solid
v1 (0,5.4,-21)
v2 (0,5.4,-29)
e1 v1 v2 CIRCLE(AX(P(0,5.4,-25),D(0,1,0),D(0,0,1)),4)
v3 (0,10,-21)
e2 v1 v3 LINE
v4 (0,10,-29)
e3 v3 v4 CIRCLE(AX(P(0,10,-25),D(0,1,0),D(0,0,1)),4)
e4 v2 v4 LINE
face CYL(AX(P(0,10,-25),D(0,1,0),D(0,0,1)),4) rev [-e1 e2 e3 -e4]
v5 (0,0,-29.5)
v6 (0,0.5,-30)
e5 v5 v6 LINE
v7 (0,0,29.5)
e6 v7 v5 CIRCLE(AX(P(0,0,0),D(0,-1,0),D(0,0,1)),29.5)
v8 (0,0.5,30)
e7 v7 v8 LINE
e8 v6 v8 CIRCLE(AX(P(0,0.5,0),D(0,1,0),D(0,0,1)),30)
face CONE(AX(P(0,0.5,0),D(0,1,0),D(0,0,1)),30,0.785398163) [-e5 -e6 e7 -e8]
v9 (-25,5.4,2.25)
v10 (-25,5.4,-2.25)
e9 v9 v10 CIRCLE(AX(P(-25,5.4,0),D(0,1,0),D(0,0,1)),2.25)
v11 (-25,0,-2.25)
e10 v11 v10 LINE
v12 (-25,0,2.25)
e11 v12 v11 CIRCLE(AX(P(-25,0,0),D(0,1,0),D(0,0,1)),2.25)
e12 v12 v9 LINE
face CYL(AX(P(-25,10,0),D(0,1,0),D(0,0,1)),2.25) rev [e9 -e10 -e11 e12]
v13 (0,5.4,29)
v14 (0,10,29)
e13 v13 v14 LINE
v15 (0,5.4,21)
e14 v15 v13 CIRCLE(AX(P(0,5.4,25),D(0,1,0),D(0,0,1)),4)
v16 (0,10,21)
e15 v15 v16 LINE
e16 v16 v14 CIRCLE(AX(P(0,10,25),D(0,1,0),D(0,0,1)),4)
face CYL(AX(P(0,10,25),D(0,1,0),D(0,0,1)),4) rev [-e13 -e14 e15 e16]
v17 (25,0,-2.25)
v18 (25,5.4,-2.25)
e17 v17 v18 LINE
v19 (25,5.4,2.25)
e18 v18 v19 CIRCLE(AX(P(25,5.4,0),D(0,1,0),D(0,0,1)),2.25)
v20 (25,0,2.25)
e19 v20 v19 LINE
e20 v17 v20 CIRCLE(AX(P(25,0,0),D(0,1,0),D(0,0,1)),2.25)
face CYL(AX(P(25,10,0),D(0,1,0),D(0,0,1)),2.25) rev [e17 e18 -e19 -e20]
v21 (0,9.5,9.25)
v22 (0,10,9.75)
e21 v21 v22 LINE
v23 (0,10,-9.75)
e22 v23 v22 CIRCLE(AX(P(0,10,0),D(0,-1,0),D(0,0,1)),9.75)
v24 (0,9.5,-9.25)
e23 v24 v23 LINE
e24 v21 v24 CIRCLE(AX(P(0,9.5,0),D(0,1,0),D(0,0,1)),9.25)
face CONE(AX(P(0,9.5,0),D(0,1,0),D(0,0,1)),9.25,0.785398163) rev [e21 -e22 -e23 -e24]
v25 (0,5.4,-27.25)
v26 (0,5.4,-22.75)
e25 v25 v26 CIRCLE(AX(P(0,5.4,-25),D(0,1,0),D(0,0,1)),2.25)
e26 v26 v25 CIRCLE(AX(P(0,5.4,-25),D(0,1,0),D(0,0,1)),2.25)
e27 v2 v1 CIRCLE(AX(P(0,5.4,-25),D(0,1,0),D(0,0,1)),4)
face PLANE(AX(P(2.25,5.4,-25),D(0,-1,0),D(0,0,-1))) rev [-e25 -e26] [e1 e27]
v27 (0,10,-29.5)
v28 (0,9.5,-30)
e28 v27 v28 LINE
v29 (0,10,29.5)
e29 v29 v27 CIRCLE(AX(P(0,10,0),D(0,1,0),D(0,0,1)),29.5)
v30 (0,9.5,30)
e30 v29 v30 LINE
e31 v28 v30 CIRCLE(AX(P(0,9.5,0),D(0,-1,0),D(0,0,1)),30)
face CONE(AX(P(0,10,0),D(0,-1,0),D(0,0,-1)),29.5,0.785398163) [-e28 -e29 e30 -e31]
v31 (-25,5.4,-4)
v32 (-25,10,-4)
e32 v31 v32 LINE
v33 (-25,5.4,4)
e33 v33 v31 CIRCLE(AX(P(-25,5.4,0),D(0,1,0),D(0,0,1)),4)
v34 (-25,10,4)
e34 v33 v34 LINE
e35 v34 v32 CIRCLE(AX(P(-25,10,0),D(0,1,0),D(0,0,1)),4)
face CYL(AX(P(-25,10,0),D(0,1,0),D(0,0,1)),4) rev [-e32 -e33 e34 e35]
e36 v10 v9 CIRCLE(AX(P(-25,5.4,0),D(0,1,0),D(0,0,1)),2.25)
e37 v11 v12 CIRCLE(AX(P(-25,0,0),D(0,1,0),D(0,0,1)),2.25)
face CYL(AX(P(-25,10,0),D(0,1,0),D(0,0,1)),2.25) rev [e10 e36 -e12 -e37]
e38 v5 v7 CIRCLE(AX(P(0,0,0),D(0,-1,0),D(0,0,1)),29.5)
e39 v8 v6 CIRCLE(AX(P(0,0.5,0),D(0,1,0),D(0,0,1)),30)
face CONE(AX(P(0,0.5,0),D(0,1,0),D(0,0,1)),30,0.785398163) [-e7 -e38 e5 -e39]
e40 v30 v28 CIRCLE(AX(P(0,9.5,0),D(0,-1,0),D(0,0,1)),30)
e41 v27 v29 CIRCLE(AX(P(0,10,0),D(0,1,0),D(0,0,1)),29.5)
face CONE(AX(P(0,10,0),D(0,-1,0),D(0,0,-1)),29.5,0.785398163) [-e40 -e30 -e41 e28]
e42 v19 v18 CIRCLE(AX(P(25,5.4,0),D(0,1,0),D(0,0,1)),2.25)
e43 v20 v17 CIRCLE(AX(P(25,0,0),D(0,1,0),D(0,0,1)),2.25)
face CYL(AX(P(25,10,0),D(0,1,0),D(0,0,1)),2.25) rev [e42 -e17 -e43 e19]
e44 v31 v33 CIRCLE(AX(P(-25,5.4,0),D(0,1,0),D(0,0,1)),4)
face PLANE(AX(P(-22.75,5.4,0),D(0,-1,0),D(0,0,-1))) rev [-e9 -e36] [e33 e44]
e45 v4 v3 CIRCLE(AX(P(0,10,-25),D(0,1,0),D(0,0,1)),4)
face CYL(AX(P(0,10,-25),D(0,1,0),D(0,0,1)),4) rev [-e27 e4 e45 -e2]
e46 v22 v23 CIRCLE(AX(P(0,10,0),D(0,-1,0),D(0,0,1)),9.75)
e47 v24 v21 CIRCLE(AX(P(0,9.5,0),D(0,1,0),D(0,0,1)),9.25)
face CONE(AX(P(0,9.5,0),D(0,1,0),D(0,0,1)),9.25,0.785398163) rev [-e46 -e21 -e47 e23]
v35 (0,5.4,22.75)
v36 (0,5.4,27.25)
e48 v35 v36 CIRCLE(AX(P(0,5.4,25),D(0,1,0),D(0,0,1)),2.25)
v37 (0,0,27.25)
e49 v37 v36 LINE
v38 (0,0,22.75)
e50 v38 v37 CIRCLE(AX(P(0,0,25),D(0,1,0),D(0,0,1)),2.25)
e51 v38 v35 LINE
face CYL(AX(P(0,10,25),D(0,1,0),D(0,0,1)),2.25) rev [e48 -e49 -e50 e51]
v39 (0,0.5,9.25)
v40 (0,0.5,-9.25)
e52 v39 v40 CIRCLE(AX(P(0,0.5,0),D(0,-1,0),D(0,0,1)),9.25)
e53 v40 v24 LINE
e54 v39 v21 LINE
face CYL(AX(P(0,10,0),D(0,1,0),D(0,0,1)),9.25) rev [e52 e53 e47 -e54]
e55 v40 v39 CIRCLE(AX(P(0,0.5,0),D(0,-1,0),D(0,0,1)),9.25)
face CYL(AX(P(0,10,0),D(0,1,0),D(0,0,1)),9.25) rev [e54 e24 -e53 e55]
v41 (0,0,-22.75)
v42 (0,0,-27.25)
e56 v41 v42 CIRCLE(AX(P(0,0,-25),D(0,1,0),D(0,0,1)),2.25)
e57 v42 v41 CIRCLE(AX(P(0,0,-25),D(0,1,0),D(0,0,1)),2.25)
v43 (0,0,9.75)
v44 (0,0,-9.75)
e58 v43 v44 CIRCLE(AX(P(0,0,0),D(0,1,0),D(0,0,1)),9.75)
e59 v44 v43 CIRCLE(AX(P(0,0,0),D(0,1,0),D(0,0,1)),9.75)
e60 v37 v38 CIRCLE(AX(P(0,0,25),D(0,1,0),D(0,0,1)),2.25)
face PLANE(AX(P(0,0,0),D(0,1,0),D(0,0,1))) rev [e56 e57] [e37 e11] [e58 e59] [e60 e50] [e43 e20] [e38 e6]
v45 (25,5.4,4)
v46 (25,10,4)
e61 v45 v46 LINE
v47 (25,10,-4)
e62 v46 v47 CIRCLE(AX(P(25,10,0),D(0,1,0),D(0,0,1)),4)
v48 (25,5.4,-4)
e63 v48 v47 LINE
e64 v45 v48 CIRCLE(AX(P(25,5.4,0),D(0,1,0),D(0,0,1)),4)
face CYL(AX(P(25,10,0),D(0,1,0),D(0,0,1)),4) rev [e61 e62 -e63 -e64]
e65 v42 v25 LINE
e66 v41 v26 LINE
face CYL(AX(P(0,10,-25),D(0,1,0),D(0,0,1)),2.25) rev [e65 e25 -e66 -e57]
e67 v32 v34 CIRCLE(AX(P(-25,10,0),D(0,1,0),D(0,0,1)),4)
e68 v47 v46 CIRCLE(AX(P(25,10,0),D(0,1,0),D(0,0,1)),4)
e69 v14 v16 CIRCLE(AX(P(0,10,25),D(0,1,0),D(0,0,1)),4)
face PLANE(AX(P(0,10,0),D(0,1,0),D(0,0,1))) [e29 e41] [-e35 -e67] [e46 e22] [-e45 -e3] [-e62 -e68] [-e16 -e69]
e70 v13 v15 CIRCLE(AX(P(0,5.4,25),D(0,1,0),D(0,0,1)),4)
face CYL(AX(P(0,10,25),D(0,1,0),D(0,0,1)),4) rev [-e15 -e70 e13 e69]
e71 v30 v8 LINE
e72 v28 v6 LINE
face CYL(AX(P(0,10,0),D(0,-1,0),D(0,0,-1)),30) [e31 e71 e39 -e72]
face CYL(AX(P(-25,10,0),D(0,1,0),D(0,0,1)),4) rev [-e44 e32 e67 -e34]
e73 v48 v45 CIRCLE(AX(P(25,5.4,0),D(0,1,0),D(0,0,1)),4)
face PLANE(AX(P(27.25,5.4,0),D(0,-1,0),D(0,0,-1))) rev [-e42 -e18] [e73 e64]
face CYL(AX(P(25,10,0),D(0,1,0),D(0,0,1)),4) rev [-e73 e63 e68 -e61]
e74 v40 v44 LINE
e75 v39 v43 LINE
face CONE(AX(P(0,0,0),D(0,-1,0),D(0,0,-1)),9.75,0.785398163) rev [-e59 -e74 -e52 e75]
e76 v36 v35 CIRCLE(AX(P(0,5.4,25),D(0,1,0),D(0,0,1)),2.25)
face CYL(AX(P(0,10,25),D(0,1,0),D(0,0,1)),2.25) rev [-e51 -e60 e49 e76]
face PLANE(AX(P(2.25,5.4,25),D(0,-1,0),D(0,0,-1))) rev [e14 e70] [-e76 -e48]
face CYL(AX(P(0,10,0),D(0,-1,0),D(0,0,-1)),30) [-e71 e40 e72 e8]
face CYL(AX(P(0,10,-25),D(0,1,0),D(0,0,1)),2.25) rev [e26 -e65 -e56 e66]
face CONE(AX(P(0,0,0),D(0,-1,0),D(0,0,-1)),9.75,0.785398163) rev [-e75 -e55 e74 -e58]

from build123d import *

# Parameters (mm, degrees)
SKETCH_1_R                = 30
EXTRUDE_1_DEPTH           = 10
M20X1_5_1_D               = 18.5
HOLE_WIZARD_1_D           = 4.5
HOLE_WIZARD_1_CBORE_D     = 8
HOLE_WIZARD_1_CBORE_DEPTH = 4.6
CHAMFER_1_SIZE            = 0.5


with BuildPart() as part:
    # 草图1 → 凸台-拉伸1 (new body)
    with BuildSketch(Plane(origin=(0, 0, 0), x_dir=(1, 0, 0), z_dir=(0, 1, 0))):
        with Locations(Location((0, 0, 0), (0, 0, 270))):
            Circle(SKETCH_1_R)
    extrude(amount=EXTRUDE_1_DEPTH)

    # M20x1.5 螺纹孔1 (through all)
    with Locations(Plane(origin=(0, 10, 0), x_dir=(1, 0, 0), z_dir=(0, 1, 0))):
        with Locations((0, 0)):
            Hole(M20X1_5_1_D / 2)

    # 打孔尺寸(%根据)内六角圆柱头螺钉的类型1 (through all)
    with Locations(Plane(origin=(0, 10, 0), x_dir=(1, 0, 0), z_dir=(0, 1, 0))):
        with Locations((0, 25), (25, 0), (0, -25), (-25, 0)):
            CounterBoreHole(HOLE_WIZARD_1_D / 2, HOLE_WIZARD_1_CBORE_D / 2, HOLE_WIZARD_1_CBORE_DEPTH)

    # 倒角1
    chamfer_1_edges = [part.edges().sort_by_distance(p)[0] for p in [
        (0, 0, -30),
        (0, 10, -30),
        (9.25, 10, 0),
        (9.25, 0, 0),
    ]]
    chamfer(chamfer_1_edges, length=CHAMFER_1_SIZE)


solid = part.part
